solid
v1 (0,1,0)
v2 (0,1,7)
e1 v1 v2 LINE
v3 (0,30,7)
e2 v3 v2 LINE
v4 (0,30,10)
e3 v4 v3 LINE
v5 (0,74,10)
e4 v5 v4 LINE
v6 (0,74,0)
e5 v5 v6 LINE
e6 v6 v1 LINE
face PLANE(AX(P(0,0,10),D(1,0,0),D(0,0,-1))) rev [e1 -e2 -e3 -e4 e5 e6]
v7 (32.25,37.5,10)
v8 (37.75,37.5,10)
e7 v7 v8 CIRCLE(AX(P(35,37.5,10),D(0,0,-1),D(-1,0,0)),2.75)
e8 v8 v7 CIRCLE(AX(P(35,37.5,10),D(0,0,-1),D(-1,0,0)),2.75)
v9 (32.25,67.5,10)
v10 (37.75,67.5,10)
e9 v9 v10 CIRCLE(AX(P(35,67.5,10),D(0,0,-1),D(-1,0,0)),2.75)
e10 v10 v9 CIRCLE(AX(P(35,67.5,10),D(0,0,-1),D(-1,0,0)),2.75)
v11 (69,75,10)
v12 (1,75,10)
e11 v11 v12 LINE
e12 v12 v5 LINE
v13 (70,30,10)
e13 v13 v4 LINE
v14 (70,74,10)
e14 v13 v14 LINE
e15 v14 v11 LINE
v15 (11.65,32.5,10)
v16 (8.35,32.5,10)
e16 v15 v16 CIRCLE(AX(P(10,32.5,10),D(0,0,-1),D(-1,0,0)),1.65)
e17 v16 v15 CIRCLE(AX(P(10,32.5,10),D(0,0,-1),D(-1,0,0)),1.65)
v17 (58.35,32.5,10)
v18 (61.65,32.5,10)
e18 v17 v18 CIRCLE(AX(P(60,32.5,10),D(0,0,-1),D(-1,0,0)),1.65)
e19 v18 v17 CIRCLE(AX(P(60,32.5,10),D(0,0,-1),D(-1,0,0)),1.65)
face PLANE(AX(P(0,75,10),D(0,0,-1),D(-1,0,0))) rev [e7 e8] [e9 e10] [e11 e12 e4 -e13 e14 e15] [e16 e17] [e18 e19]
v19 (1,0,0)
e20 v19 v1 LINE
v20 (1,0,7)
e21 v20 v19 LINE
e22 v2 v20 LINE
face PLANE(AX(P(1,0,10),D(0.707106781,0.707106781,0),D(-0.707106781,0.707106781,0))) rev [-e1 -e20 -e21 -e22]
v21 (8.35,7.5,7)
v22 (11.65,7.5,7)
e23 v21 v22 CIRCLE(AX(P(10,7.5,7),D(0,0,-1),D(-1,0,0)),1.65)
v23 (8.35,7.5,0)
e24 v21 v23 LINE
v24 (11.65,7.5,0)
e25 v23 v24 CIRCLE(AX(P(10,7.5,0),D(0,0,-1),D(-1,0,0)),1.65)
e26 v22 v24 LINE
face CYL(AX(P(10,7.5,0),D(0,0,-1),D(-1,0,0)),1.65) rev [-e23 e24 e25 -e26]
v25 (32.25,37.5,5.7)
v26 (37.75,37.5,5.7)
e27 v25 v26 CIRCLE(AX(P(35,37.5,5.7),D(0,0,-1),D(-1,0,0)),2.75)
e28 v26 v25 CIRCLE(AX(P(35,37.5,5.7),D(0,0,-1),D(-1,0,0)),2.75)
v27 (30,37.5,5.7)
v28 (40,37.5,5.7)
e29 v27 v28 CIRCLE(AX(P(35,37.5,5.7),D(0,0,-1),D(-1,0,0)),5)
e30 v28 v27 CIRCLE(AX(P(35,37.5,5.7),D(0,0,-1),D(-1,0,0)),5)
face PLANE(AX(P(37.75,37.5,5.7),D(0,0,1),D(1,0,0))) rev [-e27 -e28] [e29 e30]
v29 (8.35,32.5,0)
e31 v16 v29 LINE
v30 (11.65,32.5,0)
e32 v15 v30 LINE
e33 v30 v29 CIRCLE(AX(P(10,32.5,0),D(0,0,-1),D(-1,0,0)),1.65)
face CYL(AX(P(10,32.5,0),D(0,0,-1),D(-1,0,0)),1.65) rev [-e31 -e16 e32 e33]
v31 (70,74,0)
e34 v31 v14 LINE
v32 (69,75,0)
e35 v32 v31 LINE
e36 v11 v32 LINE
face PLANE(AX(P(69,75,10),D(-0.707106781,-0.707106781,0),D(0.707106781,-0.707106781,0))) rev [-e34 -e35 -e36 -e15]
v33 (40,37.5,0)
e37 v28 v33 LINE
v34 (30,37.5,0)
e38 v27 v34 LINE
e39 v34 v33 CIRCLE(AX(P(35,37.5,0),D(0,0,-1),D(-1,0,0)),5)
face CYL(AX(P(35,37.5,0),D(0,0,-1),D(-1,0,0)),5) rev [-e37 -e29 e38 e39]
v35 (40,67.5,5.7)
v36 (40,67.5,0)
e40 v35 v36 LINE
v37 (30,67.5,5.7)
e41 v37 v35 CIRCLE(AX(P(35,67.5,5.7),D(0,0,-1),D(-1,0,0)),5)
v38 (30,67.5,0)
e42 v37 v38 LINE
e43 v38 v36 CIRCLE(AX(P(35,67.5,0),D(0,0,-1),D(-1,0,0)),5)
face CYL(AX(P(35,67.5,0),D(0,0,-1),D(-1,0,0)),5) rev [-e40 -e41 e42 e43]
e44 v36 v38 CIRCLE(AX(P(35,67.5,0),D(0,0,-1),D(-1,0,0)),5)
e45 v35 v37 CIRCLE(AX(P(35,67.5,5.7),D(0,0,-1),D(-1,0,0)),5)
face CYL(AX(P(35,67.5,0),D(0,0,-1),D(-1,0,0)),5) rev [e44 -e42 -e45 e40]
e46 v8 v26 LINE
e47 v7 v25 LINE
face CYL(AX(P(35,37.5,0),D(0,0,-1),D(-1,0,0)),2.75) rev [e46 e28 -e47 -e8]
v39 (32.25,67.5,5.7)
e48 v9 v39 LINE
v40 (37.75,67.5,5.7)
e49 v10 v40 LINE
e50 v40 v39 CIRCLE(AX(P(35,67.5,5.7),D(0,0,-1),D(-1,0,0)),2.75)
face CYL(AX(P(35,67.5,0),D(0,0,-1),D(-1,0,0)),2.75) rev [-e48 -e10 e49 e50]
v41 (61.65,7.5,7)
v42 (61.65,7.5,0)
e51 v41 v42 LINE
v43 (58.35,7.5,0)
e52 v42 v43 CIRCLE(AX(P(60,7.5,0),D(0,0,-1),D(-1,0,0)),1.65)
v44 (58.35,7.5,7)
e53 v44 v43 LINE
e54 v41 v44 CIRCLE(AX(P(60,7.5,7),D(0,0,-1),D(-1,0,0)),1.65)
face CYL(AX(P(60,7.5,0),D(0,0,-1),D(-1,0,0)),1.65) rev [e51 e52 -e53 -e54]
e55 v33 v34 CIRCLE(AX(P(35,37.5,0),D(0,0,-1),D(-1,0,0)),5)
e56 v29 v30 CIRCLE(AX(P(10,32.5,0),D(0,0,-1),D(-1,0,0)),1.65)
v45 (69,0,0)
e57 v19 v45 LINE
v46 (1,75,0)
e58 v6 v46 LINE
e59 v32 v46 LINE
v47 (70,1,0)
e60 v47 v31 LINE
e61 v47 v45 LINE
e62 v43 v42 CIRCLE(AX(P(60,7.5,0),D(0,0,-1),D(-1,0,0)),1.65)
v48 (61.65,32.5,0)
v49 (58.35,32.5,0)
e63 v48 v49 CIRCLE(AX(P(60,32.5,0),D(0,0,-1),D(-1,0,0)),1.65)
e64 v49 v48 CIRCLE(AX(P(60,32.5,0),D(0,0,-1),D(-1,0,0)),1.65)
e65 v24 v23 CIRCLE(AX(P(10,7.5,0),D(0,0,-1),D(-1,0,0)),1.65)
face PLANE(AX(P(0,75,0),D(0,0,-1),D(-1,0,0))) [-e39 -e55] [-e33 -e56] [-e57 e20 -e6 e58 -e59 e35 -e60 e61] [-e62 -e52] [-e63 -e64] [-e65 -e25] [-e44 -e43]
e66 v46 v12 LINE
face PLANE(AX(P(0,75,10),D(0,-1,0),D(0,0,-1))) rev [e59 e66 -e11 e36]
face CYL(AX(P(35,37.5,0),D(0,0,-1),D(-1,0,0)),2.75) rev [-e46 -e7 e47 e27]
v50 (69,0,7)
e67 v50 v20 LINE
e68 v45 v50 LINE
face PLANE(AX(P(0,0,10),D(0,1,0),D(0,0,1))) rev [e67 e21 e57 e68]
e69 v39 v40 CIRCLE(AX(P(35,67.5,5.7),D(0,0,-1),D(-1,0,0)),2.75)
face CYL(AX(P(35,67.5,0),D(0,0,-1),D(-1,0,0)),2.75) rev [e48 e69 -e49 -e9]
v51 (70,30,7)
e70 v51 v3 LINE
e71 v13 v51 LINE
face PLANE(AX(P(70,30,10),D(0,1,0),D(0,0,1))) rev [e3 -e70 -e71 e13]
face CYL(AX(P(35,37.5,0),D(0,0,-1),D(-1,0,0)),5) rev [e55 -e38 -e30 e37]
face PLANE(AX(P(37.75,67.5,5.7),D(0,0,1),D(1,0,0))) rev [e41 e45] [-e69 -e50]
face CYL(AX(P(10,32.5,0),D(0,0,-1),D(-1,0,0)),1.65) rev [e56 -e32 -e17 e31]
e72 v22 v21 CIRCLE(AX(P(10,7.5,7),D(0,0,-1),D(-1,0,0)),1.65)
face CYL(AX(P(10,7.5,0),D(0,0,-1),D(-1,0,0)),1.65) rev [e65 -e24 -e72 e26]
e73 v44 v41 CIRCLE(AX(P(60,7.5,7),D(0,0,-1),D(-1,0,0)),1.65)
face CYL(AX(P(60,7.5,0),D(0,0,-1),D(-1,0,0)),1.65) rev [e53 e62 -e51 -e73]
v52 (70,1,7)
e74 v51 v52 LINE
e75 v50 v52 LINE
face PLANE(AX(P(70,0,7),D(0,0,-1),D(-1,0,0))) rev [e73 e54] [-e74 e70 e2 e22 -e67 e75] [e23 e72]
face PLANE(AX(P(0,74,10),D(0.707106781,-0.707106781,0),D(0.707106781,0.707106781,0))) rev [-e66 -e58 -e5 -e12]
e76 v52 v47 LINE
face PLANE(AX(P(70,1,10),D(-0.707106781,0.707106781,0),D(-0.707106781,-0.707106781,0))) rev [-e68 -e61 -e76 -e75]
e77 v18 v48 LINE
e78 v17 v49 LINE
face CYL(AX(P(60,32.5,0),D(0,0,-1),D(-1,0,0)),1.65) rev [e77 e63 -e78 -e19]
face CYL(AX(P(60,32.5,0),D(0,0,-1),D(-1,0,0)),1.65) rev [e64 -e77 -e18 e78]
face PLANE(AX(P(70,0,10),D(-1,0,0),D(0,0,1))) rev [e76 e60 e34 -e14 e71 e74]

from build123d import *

# Parameters (mm, degrees)
SKETCH1_W                                            = 70
SKETCH1_H                                            = 75
BOSS_EXTRUDE1_DEPTH                                  = 10
SKETCH2_W                                            = 3
SKETCH2_H                                            = 30
CUT_EXTRUDE1_DEPTH                                   = 104.07764064
M4_TAPPED_HOLE1_D                                    = 3.3
M4_TAPPED_HOLE1_DEPTH                                = 11.5
M4_TAPPED_HOLE1_TIP                                  = 0.991420021
HOLE_SIZE_PER_SOCKET_HEAD_CAP_SCREW_TYPE_D           = 5.5
HOLE_SIZE_PER_SOCKET_HEAD_CAP_SCREW_TYPE_CBORE_D     = 10
HOLE_SIZE_PER_SOCKET_HEAD_CAP_SCREW_TYPE_CBORE_DEPTH = 5.7
CHAMFER1_SIZE                                        = 1


with BuildPart() as part:
    # Sketch1 → Boss-Extrude1 (new body)
    with BuildSketch(Plane.XY):
        with Locations((35, 37.5)):
            Rectangle(SKETCH1_W, SKETCH1_H)
    extrude(amount=BOSS_EXTRUDE1_DEPTH)

    # Sketch2 → Cut-Extrude1 (cut, through all)
    with BuildSketch(Plane.ZY):
        with Locations((8.5, 15)):
            Rectangle(SKETCH2_W, SKETCH2_H)
    extrude(amount=-CUT_EXTRUDE1_DEPTH, mode=Mode.SUBTRACT)

    # M4 Tapped Hole1
    with Locations(Plane(origin=(0, 0, 0), x_dir=(-1, 0, 0), z_dir=(0, 0, -1))):
        with Locations((-10, 7.5), (-10, 32.5), (-60, 7.5), (-60, 32.5)):
            Hole(M4_TAPPED_HOLE1_D / 2, depth=M4_TAPPED_HOLE1_DEPTH)
            with Locations((0, 0, -(M4_TAPPED_HOLE1_DEPTH + M4_TAPPED_HOLE1_TIP / 2))):  # 118° drill point
                Cone(0, M4_TAPPED_HOLE1_D / 2, M4_TAPPED_HOLE1_TIP, mode=Mode.SUBTRACT)

    # Hole Size per Socket Head Cap Screw Type0 (through all)
    with Locations(Plane(origin=(0, 0, 0), x_dir=(-1, 0, 0), z_dir=(0, 0, -1))):
        with Locations((-35, 37.5), (-35, 67.5)):
            CounterBoreHole(HOLE_SIZE_PER_SOCKET_HEAD_CAP_SCREW_TYPE_D / 2, HOLE_SIZE_PER_SOCKET_HEAD_CAP_SCREW_TYPE_CBORE_D / 2, HOLE_SIZE_PER_SOCKET_HEAD_CAP_SCREW_TYPE_CBORE_DEPTH)

    # Chamfer1
    chamfer1_edges = [part.edges().sort_by_distance(p)[0] for p in [
        (70, 0, 3.5),
        (0, 0, 3.5),
        (0, 75, 5),
        (70, 75, 5),
    ]]
    chamfer(chamfer1_edges, length=CHAMFER1_SIZE)


solid = part.part
